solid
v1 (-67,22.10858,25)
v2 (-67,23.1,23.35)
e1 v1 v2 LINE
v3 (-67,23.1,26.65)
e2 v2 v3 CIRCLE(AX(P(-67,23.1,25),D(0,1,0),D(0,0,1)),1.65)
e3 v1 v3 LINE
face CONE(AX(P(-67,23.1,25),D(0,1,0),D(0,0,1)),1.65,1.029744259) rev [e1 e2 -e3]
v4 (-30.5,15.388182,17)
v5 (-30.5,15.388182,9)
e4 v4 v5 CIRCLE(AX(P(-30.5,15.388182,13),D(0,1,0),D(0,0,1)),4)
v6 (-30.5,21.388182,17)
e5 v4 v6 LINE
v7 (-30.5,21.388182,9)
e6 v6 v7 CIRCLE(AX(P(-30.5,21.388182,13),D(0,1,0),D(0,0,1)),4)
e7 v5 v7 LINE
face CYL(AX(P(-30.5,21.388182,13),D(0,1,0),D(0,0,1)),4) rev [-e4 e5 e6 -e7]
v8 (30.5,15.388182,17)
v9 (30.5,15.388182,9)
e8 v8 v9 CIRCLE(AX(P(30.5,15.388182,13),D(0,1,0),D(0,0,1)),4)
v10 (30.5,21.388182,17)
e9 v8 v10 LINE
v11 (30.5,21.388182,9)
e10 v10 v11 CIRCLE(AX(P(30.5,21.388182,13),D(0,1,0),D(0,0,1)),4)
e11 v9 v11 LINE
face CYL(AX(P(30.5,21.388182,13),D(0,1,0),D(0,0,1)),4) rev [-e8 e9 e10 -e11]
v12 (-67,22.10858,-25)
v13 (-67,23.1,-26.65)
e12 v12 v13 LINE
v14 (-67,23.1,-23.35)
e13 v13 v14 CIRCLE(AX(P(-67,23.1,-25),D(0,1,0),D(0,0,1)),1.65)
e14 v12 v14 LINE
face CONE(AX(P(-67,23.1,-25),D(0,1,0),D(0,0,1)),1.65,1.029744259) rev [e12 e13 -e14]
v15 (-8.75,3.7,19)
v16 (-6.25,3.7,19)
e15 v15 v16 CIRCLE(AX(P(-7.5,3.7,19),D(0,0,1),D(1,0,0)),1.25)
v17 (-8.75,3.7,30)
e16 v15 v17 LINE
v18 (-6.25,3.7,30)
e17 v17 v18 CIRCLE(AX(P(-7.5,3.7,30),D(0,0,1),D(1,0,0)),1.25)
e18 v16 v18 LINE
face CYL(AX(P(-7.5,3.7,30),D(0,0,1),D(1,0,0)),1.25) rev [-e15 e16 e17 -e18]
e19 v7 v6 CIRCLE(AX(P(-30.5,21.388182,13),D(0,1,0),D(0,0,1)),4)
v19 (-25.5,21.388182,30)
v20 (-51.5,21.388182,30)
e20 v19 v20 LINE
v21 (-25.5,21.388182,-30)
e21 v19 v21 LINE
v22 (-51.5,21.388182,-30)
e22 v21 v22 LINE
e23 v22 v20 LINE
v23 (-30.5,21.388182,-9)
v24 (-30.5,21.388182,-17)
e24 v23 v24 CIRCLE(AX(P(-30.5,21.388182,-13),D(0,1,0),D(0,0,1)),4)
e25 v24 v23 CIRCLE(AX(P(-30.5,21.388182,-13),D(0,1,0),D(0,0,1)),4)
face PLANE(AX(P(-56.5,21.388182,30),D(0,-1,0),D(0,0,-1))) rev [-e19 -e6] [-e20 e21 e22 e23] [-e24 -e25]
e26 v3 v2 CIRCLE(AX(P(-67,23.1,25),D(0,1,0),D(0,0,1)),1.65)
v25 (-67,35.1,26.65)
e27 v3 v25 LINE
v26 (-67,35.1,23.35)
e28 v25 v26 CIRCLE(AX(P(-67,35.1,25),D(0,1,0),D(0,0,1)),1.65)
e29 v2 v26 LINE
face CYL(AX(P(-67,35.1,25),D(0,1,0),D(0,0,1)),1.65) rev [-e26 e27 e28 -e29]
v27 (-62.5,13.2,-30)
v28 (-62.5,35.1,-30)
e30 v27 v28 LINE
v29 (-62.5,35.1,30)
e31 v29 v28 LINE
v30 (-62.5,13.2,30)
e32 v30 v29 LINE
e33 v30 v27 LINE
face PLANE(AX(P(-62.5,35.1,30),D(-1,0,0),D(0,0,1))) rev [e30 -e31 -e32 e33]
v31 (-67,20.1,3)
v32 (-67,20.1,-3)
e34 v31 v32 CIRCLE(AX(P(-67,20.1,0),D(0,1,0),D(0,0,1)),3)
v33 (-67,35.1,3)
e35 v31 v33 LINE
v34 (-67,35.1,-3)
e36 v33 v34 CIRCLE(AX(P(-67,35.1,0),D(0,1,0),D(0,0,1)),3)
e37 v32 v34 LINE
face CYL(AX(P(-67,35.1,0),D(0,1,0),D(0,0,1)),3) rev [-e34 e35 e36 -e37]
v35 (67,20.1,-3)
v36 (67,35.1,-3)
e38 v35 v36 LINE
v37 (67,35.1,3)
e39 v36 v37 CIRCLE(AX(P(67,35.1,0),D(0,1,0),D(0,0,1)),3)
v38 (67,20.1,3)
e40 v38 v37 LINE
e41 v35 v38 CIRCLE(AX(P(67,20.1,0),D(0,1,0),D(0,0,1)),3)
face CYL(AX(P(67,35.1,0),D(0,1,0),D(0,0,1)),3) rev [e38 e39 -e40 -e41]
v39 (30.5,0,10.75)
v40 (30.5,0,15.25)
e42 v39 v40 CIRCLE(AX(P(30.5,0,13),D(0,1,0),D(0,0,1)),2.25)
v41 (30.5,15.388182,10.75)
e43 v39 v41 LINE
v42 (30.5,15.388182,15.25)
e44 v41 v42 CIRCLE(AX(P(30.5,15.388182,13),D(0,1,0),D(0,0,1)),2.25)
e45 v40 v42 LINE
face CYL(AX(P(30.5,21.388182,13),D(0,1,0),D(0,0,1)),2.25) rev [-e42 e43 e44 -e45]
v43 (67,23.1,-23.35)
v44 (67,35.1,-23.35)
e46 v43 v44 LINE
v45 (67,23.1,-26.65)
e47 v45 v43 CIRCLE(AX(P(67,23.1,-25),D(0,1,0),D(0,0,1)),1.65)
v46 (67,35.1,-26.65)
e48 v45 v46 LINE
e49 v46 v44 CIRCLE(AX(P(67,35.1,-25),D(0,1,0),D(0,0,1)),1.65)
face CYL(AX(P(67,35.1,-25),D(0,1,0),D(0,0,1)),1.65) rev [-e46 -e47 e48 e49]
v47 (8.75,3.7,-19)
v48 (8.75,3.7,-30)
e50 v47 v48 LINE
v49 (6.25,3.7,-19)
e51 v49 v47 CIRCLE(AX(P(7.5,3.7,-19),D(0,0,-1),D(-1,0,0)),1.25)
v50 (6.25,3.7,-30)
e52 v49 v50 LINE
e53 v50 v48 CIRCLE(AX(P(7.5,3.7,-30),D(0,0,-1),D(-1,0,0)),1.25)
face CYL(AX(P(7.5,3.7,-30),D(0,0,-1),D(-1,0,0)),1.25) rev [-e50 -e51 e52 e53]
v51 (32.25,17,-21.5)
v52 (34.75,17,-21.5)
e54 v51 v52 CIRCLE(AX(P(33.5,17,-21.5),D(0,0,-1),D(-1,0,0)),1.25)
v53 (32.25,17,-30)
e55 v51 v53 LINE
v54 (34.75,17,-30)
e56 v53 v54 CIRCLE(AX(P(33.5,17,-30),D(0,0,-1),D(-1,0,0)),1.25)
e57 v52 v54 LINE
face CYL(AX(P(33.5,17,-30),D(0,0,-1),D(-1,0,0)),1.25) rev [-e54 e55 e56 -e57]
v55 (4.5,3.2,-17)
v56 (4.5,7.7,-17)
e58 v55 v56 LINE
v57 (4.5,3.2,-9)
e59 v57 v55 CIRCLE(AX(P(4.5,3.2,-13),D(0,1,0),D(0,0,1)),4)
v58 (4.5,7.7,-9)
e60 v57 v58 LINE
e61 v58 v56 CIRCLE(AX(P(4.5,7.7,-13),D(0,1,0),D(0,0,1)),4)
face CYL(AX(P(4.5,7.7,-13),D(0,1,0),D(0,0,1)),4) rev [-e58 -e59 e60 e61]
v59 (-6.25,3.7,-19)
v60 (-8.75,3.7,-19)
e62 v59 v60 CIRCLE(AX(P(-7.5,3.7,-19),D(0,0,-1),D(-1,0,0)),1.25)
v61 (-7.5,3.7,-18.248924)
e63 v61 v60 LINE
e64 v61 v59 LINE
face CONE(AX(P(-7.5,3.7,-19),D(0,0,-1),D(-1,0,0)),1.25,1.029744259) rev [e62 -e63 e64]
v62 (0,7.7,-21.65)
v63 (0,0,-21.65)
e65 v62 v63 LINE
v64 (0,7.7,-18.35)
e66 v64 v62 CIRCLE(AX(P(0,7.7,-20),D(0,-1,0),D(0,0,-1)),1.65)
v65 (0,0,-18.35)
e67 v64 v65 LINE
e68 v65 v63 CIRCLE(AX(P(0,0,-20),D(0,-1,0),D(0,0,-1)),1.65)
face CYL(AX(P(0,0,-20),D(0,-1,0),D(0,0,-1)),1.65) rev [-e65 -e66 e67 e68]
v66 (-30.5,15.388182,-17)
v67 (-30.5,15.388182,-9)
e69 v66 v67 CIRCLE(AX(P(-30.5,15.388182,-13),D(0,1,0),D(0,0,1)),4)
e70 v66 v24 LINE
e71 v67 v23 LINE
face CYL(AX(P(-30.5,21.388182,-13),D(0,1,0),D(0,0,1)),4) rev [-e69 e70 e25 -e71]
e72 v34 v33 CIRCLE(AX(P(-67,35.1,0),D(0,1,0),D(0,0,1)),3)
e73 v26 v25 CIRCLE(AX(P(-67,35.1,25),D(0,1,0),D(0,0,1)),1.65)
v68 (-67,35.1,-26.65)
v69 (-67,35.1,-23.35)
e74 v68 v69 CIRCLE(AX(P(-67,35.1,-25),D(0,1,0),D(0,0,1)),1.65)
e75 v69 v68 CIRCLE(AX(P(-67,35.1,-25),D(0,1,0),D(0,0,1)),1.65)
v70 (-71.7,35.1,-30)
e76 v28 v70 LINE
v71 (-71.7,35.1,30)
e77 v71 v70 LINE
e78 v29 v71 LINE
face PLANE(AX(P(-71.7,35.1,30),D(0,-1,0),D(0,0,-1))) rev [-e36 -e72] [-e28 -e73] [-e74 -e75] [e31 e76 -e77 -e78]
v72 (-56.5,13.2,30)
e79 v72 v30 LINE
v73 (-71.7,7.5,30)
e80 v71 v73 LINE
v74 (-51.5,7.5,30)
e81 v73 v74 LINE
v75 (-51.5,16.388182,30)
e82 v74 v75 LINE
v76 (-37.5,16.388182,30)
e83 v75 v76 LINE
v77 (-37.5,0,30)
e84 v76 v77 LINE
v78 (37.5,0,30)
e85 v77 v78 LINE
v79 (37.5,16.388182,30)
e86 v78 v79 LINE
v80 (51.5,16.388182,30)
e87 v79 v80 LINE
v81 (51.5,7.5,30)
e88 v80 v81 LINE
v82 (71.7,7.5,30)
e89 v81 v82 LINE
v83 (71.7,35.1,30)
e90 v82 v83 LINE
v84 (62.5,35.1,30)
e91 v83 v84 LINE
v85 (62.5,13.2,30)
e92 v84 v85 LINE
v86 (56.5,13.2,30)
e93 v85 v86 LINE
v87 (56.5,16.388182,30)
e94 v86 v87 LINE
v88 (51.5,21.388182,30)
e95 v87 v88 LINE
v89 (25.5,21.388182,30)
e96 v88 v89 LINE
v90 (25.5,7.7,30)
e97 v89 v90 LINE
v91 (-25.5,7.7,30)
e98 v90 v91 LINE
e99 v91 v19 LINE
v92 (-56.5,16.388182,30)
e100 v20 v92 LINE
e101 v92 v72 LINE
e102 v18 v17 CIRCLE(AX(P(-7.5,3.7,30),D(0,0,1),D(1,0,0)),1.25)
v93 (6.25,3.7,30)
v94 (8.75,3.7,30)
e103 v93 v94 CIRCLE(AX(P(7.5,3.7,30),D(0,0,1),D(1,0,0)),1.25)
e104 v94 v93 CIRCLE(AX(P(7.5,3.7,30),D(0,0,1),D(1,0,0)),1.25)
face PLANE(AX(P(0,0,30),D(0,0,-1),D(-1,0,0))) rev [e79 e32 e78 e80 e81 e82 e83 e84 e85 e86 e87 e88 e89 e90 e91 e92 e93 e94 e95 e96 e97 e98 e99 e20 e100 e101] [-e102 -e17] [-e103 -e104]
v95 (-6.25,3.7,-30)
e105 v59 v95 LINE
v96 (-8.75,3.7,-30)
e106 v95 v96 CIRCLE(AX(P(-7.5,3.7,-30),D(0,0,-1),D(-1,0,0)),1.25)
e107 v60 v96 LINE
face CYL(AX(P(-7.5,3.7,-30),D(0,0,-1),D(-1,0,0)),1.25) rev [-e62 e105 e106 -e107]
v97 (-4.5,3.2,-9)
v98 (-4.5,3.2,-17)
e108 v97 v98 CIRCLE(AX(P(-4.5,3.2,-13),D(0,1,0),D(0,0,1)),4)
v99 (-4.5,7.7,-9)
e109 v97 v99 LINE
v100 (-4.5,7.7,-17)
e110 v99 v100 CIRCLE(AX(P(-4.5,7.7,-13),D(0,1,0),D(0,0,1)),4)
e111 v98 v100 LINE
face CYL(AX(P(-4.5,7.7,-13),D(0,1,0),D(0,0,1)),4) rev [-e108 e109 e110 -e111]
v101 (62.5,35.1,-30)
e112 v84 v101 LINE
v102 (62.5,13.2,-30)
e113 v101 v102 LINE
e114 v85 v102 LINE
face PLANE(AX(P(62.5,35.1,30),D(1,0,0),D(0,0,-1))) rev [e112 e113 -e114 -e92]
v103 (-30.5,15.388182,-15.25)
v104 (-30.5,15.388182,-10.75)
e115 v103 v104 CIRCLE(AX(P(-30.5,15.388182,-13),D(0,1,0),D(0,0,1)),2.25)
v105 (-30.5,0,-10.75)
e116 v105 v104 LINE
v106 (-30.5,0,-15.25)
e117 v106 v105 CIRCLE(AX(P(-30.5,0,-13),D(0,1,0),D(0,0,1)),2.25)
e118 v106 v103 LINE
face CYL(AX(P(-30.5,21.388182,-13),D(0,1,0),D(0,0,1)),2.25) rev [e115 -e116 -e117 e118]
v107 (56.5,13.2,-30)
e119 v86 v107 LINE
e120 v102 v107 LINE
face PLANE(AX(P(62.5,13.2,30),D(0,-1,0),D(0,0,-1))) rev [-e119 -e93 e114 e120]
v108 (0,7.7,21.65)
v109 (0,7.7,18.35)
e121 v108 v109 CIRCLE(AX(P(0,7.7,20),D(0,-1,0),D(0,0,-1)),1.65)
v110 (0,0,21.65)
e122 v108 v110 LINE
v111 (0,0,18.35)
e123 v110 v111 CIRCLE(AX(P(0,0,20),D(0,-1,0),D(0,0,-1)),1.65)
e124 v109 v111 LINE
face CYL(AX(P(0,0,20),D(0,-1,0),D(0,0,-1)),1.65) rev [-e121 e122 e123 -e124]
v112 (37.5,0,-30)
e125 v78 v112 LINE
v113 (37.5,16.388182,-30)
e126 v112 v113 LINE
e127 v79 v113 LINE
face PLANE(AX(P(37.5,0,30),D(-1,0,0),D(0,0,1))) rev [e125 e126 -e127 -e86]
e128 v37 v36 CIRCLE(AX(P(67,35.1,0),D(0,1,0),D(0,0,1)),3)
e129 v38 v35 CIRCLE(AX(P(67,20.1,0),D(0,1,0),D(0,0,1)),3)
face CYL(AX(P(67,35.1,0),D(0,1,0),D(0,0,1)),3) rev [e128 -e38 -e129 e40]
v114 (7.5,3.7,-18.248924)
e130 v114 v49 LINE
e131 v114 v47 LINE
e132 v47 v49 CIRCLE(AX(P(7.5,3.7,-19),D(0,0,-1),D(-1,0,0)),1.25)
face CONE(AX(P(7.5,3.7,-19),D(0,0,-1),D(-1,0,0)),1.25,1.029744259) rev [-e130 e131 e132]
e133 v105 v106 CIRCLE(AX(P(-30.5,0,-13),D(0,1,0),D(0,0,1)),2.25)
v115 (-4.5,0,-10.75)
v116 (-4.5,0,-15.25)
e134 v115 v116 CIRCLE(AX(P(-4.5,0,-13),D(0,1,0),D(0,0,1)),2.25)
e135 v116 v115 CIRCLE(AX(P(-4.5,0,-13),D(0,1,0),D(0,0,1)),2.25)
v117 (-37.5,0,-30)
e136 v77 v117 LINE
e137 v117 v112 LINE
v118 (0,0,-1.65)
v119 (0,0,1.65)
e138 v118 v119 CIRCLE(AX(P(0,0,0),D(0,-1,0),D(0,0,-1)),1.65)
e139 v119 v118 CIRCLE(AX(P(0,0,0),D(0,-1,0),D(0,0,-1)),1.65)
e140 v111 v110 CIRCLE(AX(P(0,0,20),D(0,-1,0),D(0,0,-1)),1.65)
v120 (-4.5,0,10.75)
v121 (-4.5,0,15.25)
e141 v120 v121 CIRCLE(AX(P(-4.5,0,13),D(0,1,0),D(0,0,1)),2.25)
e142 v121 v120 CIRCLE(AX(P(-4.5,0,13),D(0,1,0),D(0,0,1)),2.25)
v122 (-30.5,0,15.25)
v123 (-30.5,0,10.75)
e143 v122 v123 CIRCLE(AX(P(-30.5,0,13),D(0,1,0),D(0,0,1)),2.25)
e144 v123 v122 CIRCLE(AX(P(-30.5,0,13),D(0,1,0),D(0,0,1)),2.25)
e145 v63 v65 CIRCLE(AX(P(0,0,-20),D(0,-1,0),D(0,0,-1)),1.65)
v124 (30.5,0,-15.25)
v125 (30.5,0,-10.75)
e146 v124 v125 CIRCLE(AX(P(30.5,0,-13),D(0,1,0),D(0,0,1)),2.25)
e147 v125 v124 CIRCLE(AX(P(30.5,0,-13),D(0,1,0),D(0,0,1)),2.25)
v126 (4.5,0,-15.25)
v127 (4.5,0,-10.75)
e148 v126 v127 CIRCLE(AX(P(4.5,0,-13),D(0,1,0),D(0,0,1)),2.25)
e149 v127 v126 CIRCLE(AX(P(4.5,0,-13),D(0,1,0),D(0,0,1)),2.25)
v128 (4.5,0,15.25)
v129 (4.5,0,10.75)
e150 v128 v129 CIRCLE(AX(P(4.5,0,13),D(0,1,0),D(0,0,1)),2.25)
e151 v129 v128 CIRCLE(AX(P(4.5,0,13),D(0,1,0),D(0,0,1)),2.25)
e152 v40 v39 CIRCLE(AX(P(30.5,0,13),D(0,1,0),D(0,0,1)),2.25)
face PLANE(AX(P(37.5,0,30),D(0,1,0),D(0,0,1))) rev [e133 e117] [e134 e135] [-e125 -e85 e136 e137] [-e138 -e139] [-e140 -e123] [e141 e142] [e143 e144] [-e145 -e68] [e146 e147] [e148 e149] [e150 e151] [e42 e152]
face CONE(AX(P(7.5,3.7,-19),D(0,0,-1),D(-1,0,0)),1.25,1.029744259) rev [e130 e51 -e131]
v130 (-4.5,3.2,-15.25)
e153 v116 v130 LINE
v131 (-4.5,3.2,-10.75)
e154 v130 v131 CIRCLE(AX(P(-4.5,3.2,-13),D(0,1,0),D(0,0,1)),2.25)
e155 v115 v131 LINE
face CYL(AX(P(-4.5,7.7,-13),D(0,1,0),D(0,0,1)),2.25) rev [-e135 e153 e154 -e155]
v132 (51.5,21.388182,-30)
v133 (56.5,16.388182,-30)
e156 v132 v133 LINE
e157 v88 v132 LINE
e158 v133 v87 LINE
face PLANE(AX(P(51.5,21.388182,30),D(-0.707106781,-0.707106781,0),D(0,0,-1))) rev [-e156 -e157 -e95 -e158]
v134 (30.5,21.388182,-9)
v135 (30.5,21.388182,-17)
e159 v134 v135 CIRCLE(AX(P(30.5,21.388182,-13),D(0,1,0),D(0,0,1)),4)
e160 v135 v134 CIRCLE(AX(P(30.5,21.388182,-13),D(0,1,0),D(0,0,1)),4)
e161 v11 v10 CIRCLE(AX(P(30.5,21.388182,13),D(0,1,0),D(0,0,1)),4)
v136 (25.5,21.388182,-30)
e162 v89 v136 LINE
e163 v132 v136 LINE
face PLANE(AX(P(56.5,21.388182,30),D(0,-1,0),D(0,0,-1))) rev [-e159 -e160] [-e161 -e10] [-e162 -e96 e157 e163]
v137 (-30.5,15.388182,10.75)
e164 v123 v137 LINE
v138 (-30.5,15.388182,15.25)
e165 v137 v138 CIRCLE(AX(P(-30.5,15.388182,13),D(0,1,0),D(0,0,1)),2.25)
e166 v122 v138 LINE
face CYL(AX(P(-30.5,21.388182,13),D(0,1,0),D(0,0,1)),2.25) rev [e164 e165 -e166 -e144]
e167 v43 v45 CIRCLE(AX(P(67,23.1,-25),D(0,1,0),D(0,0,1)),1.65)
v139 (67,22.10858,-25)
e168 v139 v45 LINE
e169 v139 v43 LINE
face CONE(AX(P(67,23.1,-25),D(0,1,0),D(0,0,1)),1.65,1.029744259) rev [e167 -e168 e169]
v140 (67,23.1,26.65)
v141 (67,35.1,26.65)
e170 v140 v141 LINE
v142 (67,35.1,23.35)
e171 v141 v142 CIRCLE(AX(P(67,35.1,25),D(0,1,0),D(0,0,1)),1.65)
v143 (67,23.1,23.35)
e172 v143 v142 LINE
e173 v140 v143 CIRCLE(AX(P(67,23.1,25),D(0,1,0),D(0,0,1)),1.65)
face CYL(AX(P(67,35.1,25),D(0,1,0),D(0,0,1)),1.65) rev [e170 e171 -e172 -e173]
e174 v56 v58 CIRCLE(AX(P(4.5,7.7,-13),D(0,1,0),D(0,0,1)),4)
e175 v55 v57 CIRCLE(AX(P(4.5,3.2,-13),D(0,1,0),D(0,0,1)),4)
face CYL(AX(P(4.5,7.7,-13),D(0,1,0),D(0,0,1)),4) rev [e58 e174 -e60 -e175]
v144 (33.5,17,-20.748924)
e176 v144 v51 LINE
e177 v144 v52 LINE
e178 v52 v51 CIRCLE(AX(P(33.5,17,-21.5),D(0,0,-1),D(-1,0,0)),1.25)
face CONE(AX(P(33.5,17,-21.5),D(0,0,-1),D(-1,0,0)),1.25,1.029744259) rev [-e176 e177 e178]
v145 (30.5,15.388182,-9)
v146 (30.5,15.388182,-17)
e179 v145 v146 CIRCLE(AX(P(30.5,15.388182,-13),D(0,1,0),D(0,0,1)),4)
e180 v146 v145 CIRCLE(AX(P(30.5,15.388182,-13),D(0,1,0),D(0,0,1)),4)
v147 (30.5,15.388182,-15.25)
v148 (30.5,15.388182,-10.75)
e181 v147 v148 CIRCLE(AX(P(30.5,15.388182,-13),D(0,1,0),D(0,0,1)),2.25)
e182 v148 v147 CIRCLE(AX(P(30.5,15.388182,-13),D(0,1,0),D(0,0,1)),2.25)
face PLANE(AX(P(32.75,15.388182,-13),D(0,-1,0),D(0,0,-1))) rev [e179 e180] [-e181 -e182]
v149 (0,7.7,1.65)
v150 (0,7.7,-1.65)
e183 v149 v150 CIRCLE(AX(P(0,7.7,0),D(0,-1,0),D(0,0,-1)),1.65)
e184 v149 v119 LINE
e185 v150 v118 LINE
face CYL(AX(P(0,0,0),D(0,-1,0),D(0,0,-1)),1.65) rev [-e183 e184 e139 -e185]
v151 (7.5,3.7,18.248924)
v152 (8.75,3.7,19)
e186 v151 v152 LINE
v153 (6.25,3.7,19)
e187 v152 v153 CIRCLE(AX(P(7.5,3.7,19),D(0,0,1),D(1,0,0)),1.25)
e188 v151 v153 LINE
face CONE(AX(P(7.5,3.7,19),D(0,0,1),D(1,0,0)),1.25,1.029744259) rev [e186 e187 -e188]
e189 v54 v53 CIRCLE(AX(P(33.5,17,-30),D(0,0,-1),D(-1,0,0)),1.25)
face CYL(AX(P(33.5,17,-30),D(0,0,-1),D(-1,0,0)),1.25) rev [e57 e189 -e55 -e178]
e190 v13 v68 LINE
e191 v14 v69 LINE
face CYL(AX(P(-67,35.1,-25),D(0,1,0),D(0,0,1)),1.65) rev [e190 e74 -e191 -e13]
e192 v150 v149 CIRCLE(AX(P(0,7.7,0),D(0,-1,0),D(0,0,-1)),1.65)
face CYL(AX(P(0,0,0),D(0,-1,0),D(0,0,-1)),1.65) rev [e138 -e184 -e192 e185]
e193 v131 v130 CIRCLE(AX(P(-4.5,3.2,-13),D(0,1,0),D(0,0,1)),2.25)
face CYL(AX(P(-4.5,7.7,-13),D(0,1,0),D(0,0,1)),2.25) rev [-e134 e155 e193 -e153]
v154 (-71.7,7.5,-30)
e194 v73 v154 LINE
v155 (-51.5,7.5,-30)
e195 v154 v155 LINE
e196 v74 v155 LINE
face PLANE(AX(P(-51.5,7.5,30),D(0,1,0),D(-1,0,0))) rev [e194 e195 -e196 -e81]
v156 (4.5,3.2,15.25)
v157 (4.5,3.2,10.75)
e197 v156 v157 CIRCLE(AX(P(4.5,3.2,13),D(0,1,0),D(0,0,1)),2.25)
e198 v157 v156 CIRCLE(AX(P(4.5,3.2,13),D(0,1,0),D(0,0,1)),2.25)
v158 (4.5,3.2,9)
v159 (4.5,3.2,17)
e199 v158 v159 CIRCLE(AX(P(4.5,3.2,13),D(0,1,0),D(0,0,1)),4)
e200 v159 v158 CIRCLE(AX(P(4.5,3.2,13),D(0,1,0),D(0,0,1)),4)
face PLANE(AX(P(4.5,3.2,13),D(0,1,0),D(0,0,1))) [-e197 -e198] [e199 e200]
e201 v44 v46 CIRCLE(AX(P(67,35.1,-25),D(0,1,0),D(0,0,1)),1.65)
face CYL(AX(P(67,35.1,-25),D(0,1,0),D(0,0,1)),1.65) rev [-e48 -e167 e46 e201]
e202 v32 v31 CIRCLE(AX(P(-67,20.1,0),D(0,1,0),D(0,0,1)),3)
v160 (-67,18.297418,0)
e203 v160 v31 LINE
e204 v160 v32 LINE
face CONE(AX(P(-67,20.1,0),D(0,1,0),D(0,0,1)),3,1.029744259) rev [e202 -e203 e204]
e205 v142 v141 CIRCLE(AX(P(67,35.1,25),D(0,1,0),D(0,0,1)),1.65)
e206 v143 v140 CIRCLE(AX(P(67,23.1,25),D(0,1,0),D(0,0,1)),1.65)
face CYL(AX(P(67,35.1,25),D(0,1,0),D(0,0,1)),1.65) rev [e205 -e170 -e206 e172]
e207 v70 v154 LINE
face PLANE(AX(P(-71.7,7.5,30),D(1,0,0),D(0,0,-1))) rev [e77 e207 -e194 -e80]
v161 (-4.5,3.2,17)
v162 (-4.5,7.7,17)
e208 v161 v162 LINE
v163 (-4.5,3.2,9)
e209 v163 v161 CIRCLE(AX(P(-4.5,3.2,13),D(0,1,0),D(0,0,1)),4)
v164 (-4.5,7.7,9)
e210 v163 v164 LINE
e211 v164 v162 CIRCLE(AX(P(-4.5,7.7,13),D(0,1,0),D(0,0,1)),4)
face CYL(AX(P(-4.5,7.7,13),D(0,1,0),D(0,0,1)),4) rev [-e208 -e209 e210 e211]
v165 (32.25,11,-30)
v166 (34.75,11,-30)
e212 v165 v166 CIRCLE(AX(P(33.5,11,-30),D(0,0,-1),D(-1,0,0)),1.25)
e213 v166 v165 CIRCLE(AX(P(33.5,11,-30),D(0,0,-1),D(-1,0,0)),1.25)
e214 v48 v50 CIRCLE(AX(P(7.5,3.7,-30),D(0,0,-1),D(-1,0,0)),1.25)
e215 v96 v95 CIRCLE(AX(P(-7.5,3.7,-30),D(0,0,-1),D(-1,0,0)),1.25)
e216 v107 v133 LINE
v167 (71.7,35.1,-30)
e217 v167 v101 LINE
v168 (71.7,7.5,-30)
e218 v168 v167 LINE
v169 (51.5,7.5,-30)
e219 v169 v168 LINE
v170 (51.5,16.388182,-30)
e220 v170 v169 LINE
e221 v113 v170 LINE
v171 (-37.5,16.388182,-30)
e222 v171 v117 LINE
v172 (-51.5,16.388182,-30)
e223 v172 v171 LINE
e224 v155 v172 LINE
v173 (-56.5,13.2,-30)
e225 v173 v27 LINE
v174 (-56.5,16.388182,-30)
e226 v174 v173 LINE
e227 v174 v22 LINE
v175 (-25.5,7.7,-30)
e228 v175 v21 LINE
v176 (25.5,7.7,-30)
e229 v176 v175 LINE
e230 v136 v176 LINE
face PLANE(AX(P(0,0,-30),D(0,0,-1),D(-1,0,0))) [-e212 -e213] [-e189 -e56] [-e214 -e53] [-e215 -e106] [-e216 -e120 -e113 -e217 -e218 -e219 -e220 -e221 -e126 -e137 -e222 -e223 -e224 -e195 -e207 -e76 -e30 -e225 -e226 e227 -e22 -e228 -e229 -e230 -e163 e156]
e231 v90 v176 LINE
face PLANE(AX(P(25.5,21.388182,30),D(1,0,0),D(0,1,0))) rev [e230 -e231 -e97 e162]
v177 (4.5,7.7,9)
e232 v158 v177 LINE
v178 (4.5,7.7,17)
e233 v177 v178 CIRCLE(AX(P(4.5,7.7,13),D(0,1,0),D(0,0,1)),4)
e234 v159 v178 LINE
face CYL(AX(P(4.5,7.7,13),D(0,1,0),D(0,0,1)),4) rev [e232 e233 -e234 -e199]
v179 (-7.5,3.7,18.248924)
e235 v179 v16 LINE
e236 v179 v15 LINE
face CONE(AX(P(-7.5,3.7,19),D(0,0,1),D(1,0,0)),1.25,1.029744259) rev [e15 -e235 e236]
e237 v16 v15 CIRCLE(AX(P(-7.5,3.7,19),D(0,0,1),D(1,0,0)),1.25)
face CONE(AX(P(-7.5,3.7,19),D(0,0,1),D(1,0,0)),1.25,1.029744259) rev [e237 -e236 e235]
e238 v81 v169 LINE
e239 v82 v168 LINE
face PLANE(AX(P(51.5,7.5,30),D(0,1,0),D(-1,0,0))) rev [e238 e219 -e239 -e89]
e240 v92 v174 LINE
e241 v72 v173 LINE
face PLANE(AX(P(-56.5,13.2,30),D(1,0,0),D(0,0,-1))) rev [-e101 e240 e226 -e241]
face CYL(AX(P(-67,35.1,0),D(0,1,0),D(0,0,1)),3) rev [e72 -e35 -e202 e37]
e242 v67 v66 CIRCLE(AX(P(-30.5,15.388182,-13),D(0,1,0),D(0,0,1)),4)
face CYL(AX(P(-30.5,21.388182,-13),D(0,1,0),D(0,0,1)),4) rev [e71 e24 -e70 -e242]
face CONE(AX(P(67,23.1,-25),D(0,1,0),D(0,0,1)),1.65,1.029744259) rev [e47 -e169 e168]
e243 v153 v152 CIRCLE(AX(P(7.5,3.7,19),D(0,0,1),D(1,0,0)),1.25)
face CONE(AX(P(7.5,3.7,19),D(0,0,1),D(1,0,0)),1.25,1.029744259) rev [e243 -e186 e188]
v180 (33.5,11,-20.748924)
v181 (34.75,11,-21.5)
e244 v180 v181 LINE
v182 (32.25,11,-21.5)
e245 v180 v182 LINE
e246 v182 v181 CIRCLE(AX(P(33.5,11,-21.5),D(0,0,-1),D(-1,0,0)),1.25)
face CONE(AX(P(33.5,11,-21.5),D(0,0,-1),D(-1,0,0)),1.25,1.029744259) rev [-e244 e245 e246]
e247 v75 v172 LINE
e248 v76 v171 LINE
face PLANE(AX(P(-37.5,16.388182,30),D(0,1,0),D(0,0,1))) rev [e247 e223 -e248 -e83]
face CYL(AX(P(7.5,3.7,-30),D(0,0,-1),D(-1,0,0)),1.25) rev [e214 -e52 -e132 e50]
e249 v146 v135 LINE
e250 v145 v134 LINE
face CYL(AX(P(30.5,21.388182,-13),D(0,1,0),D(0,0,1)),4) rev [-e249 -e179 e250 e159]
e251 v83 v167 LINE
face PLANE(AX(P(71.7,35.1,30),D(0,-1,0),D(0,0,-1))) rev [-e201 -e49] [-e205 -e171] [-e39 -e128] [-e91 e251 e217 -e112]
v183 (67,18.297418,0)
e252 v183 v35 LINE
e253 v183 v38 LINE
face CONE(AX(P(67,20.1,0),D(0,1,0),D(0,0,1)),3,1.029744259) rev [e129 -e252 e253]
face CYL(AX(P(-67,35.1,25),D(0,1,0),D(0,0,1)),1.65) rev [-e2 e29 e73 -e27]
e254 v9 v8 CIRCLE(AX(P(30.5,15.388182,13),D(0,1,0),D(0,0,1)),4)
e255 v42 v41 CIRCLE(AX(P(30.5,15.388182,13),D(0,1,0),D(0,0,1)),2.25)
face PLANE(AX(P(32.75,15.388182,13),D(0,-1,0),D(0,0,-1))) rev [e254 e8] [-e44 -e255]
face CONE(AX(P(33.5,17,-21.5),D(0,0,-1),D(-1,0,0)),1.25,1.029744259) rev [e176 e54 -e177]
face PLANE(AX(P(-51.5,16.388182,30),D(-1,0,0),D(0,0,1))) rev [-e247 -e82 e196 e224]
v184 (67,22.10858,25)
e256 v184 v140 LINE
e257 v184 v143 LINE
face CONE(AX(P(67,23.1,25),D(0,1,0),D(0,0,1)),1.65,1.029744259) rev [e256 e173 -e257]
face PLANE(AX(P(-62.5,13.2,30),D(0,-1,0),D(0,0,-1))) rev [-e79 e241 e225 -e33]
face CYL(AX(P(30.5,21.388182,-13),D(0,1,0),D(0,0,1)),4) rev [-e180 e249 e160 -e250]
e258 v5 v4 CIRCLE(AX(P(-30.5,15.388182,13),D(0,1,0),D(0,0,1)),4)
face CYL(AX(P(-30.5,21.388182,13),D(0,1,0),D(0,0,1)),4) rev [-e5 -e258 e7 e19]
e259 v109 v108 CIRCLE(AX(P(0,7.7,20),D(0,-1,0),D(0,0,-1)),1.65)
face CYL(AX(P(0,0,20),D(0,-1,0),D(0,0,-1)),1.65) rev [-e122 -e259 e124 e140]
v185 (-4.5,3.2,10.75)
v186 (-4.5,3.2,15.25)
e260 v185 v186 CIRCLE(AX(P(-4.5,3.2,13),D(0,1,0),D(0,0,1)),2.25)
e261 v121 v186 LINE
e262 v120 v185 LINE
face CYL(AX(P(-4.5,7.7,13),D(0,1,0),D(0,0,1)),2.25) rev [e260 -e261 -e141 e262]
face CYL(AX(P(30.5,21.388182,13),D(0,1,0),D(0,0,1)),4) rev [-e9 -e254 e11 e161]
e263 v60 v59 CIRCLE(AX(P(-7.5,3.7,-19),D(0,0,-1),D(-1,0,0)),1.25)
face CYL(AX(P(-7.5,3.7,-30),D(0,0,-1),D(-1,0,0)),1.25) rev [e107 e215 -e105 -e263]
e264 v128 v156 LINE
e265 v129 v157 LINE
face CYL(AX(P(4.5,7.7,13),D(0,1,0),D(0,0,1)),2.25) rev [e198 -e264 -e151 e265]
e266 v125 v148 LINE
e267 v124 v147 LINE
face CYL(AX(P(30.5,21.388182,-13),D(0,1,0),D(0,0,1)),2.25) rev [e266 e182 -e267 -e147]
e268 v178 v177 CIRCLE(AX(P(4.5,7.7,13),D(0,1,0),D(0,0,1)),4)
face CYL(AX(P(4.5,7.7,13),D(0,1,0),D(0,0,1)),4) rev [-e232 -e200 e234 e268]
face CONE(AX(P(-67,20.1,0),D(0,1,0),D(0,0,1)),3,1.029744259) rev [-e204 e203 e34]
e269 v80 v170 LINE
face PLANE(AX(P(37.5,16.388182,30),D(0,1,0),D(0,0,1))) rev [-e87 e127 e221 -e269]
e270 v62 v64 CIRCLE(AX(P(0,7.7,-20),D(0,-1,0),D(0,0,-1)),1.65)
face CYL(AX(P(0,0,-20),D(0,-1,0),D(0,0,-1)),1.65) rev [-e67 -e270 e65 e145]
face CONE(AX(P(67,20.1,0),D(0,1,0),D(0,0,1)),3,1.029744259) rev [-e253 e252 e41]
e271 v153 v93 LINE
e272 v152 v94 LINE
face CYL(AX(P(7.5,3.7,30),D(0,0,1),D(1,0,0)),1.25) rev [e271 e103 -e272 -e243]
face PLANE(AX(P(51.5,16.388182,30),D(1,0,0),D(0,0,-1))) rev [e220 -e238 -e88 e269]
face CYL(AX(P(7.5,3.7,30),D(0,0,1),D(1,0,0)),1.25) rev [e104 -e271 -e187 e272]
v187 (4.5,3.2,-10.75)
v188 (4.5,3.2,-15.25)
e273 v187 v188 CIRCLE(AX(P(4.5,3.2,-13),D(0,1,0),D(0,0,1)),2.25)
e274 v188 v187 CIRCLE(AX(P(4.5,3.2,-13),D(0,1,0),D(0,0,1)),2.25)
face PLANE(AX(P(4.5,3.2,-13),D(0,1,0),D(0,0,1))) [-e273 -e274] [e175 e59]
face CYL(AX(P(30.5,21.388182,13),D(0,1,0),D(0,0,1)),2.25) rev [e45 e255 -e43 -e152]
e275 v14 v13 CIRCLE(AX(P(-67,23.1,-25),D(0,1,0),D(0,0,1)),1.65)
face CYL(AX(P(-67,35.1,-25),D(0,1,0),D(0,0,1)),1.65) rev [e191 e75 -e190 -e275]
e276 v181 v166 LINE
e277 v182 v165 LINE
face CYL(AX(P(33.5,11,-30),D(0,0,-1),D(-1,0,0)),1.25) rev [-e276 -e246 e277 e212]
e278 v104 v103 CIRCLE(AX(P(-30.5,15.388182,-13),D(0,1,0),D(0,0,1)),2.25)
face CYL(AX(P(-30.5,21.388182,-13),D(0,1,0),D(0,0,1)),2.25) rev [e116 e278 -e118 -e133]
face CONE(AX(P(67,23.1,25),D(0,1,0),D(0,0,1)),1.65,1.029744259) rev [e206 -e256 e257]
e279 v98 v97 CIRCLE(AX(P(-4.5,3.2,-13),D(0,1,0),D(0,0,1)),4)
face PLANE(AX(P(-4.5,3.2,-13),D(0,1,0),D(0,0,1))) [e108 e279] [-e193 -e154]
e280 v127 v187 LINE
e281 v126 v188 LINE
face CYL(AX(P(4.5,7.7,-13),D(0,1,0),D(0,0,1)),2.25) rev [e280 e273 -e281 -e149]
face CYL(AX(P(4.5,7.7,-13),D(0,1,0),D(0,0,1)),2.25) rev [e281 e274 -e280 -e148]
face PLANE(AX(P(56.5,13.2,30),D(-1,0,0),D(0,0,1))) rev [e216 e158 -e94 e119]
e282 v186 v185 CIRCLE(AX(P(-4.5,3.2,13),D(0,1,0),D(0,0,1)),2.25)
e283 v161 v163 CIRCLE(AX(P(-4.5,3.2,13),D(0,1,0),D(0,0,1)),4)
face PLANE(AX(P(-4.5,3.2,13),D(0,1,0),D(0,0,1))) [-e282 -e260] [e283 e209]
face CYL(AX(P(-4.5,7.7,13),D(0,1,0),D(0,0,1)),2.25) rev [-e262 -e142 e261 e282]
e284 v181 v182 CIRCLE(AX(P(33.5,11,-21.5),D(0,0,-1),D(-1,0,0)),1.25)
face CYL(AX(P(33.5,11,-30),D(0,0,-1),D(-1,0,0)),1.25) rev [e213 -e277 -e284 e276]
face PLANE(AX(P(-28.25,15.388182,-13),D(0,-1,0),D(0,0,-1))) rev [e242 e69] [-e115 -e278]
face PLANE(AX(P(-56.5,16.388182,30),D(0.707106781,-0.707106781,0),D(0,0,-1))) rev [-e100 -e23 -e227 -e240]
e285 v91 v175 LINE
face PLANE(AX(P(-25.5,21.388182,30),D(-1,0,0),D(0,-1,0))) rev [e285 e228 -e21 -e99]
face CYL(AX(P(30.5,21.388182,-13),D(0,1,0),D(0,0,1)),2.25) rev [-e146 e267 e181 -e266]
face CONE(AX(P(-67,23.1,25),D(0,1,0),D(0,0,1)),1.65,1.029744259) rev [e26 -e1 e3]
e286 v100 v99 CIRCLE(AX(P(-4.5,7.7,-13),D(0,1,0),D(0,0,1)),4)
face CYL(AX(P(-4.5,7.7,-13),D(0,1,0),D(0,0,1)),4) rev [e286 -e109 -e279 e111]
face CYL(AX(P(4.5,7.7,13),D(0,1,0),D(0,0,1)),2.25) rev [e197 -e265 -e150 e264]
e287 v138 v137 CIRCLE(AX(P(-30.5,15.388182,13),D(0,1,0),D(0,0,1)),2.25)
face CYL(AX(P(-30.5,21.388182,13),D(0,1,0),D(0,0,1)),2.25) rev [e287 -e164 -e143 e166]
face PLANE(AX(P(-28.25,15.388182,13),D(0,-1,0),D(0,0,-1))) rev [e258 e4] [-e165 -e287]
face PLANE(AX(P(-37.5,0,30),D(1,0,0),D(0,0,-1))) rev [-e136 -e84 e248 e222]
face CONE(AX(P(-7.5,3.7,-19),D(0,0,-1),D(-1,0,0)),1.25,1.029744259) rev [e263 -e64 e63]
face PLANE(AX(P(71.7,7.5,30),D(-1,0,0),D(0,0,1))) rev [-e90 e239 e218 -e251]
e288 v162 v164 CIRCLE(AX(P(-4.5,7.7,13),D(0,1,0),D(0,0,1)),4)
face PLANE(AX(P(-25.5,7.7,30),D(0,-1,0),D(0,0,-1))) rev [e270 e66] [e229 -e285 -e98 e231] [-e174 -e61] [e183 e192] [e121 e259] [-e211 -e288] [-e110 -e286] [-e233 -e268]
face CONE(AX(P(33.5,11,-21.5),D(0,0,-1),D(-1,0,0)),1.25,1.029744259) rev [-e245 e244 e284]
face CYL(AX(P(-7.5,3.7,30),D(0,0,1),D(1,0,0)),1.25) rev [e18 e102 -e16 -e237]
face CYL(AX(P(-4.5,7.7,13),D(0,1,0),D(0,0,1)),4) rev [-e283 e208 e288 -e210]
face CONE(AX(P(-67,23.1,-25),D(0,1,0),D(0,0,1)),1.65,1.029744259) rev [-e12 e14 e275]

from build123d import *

# Parameters (mm, degrees)
EXTRUDE_1_DEPTH             = 30
CHAMFER_1_SIZE              = 5
SKETCH_2_R                  = 2
CUT_EXTRUDE_1_DEPTH         = 86.28129924
SKETCH_4_R                  = 3.5
CUT_EXTRUDE_3_DEPTH         = 4.5
SKETCH_5_R                  = 3.5
CUT_EXTRUDE_4_DEPTH         = 4.5
HOLE_WIZARD_M3_5_D          = 2.5
HOLE_WIZARD_M3_5_DEPTH      = 8.5
HOLE_WIZARD_M3_5_TIP        = 0.751075774
HOLE_WIZARD_M4_2_D          = 3.3
HOLE_WIZARD_2_D             = 4.5
HOLE_WIZARD_2_CBORE_D       = 8
HOLE_WIZARD_2_CBORE_DEPTH   = 6
HOLE_WIZARD_2_2_D           = 4.5
HOLE_WIZARD_2_2_CBORE_D     = 8
HOLE_WIZARD_2_2_CBORE_DEPTH = 4.5
PATTERN_LINEAR_1_COUNT      = 3
PATTERN_LINEAR_1_PITCH      = 20


with BuildPart() as part:
    # 草图1 → 凸台-拉伸1 (new, symmetric)
    with BuildSketch(Plane.XY):
        Polygon((37.5, 0), (-37.5, 0), (-37.5, 16.388182382), (-51.5, 16.388182382), (-51.5, 7.5), (-71.7, 7.5), (-71.7, 35.1), (-62.5, 35.1), (-62.5, 13.2), (-56.5, 13.2), (-56.5, 21.388182382), (-25.5, 21.388182382), (-25.5, 7.7), (25.5, 7.7), (25.5, 21.388182382), (56.5, 21.388182382), (56.5, 13.2), (62.5, 13.2), (62.5, 35.1), (71.7, 35.1), (71.7, 7.5), (51.5, 7.5), (51.5, 16.388182382), (37.5, 16.388182382), align=None)
    extrude(amount=EXTRUDE_1_DEPTH, both=True)

    # 倒角1
    chamfer_1_edges = [part.edges().sort_by_distance(p)[0] for p in [
        (-56.5, 21.388182382, 0),
        (56.5, 21.388182382, 0),
    ]]
    chamfer(chamfer_1_edges, length=CHAMFER_1_SIZE)

    # 草图2 → 切除-拉伸1 (cut, through all)
    with BuildSketch(Plane.XZ):
        with Locations(Location((-4.5, 13, 0), (0, 0, 270))):
            Circle(SKETCH_2_R)
        with Locations(Location((-30.5, 13, 0), (0, 0, 270))):
            Circle(SKETCH_2_R)
        with Locations(Location((30.5, 13, 0), (0, 0, 270))):
            Circle(SKETCH_2_R)
        with Locations(Location((4.5, 13, 0), (0, 0, 270))):
            Circle(SKETCH_2_R)
        with Locations(Location((4.5, -13, 0), (0, 0, 270))):
            Circle(SKETCH_2_R)
        with Locations(Location((30.5, -13, 0), (0, 0, 270))):
            Circle(SKETCH_2_R)
        with Locations(Location((-30.5, -13, 0), (0, 0, 270))):
            Circle(SKETCH_2_R)
        with Locations(Location((-4.5, -13, 0), (0, 0, 270))):
            Circle(SKETCH_2_R)
    extrude(amount=-CUT_EXTRUDE_1_DEPTH, mode=Mode.SUBTRACT)

    # 草图4 → 切除-拉伸3 (cut)
    with BuildSketch(Plane(origin=(0, 21.388182382, 0), x_dir=(1, 0, 0), z_dir=(0, 1, 0))):
        with Locations(Location((-30.5, 13, 0), (0, 0, 270))):
            Circle(SKETCH_4_R)
        with Locations(Location((-30.5, -13, 0), (0, 0, 270))):
            Circle(SKETCH_4_R)
        with Locations(Location((30.5, 13, 0), (0, 0, 270))):
            Circle(SKETCH_4_R)
        with Locations(Location((30.5, -13, 0), (0, 0, 270))):
            Circle(SKETCH_4_R)
    extrude(amount=-CUT_EXTRUDE_3_DEPTH, mode=Mode.SUBTRACT)

    # 草图5 → 切除-拉伸4 (cut)
    with BuildSketch(Plane(origin=(0, 7.7, 0), x_dir=(1, 0, 0), z_dir=(0, 1, 0))):
        with Locations(Location((-4.5, 13, 0), (0, 0, 270))):
            Circle(SKETCH_5_R)
        with Locations(Location((4.5, 13, 0), (0, 0, 270))):
            Circle(SKETCH_5_R)
        with Locations(Location((4.5, -13, 0), (0, 0, 270))):
            Circle(SKETCH_5_R)
        with Locations(Location((-4.5, -13, 0), (0, 0, 270))):
            Circle(SKETCH_5_R)
    extrude(amount=-CUT_EXTRUDE_4_DEPTH, mode=Mode.SUBTRACT)

    # 草图6 → M4 螺纹孔1 (revolve, cut)
    with BuildSketch(Plane(origin=(-67, 35.1, -25), x_dir=(0, 0, 1), z_dir=(1, 0, 0))):
        Polygon((0, 0), (0, 12.991420021), (1.65, 12), (1.65, 0), align=None)
    hole_wizard_m4_1 = revolve(axis=Axis((-67, 41.45, -25), (0, -1, 0)), mode=Mode.SUBTRACT)

    # 镜向1: M4 螺纹孔1 across plane
    add(hole_wizard_m4_1.mirror(Plane.XY), mode=Mode.SUBTRACT)

    # 镜向2: M4 螺纹孔1 across plane
    add(hole_wizard_m4_1.mirror(Plane(origin=(0, 0, 0), x_dir=(0, 0, 1), z_dir=(1, 0, 0))), mode=Mode.SUBTRACT)

    # 镜向2 copy 1 sketch → 镜向2 copy 1 (revolve, cut)
    with BuildSketch(Plane(origin=(67, 35.1, 25), x_dir=(0, 0, -1), z_dir=(-1, 0, 0))):
        Polygon((0, 0), (0, 12.991420021), (1.65, 12), (1.65, 0), align=None)
    revolve(axis=Axis((67, 41.45, 25), (0, -1, 0)), mode=Mode.SUBTRACT)

    # M3 螺纹孔5
    with Locations(Plane(origin=(0, 0, -30), x_dir=(-1, 0, 0), z_dir=(0, 0, -1))):
        with Locations((-33.5, 11), (-33.5, 17)):
            Hole(HOLE_WIZARD_M3_5_D / 2, depth=HOLE_WIZARD_M3_5_DEPTH)
            with Locations((0, 0, -(HOLE_WIZARD_M3_5_DEPTH + HOLE_WIZARD_M3_5_TIP / 2))):  # 118° drill point
                Cone(0, HOLE_WIZARD_M3_5_D / 2, HOLE_WIZARD_M3_5_TIP, mode=Mode.SUBTRACT)

    # M4 螺纹孔2 (through all)
    with Locations(Plane(origin=(0, 0, 0), x_dir=(-1, 0, 0), z_dir=(0, -1, 0))):
        with Locations((0, 20)):
            hole_wizard_m4_2 = Hole(HOLE_WIZARD_M4_2_D / 2)

    # 草图14 → M3 螺纹孔3 (revolve, cut)
    with BuildSketch(Plane(origin=(-7.5, 3.7, 30), x_dir=(0, -1, 0), z_dir=(1, 0, 0))):
        Polygon((0, 0), (0, 11.751075774), (1.25, 11), (1.25, 0), align=None)
    hole_wizard_m3_3 = revolve(axis=Axis((-7.5, 3.7, 36.35), (0, 0, -1)), mode=Mode.SUBTRACT)

    # 镜向4: M3 螺纹孔3 across plane
    add(hole_wizard_m3_3.mirror(Plane(origin=(0, 0, 0), x_dir=(0, 0, 1), z_dir=(1, 0, 0))), mode=Mode.SUBTRACT)

    # 镜向5: M3 螺纹孔3 across plane
    add(hole_wizard_m3_3.mirror(Plane.XY), mode=Mode.SUBTRACT)

    # 镜向5 copy 1 sketch → 镜向5 copy 1 (revolve, cut)
    with BuildSketch(Plane(origin=(7.5, 3.7, -30), x_dir=(0, -1, 0), z_dir=(-1, 0, 0))):
        Polygon((0, 0), (0, 11.751075774), (1.25, 11), (1.25, 0), align=None)
    revolve(axis=Axis((7.5, 3.7, -36.35), (0, 0, 1)), mode=Mode.SUBTRACT)

    # Hole Wizard 2 (through all)
    with Locations(Plane(origin=(0, 21.388182382, 0), x_dir=(1, 0, 0), z_dir=(0, 1, 0))):
        with Locations((-30.5, 13), (-30.5, -13), (30.5, 13), (30.5, -13)):
            CounterBoreHole(HOLE_WIZARD_2_D / 2, HOLE_WIZARD_2_CBORE_D / 2, HOLE_WIZARD_2_CBORE_DEPTH)

    # Hole Wizard 2 2 (through all)
    with Locations(Plane(origin=(0, 7.7, 0), x_dir=(1, 0, 0), z_dir=(0, 1, 0))):
        with Locations((-4.5, 13), (4.5, 13), (-4.5, -13), (4.5, -13)):
            CounterBoreHole(HOLE_WIZARD_2_2_D / 2, HOLE_WIZARD_2_2_CBORE_D / 2, HOLE_WIZARD_2_2_CBORE_DEPTH)

    # 阵列(线性)1: M4 螺纹孔2 ×3
    with Locations(*[(0, 0, i * PATTERN_LINEAR_1_PITCH) for i in range(1, PATTERN_LINEAR_1_COUNT)]):
        add(hole_wizard_m4_2, mode=Mode.SUBTRACT)

    # 草图22 → 大小mm 暗销孔1 (revolve, cut)
    with BuildSketch(Plane(origin=(67, 35.1, 0), x_dir=(0, 0, 1), z_dir=(1, 0, 0))):
        Polygon((0, 0), (0, 16.802581857), (3, 15), (3, 0), align=None)
    mm_1 = revolve(axis=Axis((67, 41.45, 0), (0, -1, 0)), mode=Mode.SUBTRACT)

    # 镜向6: 大小mm 暗销孔1 across plane
    add(mm_1.mirror(Plane(origin=(0, 0, 0), x_dir=(0, 0, 1), z_dir=(1, 0, 0))), mode=Mode.SUBTRACT)


solid = part.part
